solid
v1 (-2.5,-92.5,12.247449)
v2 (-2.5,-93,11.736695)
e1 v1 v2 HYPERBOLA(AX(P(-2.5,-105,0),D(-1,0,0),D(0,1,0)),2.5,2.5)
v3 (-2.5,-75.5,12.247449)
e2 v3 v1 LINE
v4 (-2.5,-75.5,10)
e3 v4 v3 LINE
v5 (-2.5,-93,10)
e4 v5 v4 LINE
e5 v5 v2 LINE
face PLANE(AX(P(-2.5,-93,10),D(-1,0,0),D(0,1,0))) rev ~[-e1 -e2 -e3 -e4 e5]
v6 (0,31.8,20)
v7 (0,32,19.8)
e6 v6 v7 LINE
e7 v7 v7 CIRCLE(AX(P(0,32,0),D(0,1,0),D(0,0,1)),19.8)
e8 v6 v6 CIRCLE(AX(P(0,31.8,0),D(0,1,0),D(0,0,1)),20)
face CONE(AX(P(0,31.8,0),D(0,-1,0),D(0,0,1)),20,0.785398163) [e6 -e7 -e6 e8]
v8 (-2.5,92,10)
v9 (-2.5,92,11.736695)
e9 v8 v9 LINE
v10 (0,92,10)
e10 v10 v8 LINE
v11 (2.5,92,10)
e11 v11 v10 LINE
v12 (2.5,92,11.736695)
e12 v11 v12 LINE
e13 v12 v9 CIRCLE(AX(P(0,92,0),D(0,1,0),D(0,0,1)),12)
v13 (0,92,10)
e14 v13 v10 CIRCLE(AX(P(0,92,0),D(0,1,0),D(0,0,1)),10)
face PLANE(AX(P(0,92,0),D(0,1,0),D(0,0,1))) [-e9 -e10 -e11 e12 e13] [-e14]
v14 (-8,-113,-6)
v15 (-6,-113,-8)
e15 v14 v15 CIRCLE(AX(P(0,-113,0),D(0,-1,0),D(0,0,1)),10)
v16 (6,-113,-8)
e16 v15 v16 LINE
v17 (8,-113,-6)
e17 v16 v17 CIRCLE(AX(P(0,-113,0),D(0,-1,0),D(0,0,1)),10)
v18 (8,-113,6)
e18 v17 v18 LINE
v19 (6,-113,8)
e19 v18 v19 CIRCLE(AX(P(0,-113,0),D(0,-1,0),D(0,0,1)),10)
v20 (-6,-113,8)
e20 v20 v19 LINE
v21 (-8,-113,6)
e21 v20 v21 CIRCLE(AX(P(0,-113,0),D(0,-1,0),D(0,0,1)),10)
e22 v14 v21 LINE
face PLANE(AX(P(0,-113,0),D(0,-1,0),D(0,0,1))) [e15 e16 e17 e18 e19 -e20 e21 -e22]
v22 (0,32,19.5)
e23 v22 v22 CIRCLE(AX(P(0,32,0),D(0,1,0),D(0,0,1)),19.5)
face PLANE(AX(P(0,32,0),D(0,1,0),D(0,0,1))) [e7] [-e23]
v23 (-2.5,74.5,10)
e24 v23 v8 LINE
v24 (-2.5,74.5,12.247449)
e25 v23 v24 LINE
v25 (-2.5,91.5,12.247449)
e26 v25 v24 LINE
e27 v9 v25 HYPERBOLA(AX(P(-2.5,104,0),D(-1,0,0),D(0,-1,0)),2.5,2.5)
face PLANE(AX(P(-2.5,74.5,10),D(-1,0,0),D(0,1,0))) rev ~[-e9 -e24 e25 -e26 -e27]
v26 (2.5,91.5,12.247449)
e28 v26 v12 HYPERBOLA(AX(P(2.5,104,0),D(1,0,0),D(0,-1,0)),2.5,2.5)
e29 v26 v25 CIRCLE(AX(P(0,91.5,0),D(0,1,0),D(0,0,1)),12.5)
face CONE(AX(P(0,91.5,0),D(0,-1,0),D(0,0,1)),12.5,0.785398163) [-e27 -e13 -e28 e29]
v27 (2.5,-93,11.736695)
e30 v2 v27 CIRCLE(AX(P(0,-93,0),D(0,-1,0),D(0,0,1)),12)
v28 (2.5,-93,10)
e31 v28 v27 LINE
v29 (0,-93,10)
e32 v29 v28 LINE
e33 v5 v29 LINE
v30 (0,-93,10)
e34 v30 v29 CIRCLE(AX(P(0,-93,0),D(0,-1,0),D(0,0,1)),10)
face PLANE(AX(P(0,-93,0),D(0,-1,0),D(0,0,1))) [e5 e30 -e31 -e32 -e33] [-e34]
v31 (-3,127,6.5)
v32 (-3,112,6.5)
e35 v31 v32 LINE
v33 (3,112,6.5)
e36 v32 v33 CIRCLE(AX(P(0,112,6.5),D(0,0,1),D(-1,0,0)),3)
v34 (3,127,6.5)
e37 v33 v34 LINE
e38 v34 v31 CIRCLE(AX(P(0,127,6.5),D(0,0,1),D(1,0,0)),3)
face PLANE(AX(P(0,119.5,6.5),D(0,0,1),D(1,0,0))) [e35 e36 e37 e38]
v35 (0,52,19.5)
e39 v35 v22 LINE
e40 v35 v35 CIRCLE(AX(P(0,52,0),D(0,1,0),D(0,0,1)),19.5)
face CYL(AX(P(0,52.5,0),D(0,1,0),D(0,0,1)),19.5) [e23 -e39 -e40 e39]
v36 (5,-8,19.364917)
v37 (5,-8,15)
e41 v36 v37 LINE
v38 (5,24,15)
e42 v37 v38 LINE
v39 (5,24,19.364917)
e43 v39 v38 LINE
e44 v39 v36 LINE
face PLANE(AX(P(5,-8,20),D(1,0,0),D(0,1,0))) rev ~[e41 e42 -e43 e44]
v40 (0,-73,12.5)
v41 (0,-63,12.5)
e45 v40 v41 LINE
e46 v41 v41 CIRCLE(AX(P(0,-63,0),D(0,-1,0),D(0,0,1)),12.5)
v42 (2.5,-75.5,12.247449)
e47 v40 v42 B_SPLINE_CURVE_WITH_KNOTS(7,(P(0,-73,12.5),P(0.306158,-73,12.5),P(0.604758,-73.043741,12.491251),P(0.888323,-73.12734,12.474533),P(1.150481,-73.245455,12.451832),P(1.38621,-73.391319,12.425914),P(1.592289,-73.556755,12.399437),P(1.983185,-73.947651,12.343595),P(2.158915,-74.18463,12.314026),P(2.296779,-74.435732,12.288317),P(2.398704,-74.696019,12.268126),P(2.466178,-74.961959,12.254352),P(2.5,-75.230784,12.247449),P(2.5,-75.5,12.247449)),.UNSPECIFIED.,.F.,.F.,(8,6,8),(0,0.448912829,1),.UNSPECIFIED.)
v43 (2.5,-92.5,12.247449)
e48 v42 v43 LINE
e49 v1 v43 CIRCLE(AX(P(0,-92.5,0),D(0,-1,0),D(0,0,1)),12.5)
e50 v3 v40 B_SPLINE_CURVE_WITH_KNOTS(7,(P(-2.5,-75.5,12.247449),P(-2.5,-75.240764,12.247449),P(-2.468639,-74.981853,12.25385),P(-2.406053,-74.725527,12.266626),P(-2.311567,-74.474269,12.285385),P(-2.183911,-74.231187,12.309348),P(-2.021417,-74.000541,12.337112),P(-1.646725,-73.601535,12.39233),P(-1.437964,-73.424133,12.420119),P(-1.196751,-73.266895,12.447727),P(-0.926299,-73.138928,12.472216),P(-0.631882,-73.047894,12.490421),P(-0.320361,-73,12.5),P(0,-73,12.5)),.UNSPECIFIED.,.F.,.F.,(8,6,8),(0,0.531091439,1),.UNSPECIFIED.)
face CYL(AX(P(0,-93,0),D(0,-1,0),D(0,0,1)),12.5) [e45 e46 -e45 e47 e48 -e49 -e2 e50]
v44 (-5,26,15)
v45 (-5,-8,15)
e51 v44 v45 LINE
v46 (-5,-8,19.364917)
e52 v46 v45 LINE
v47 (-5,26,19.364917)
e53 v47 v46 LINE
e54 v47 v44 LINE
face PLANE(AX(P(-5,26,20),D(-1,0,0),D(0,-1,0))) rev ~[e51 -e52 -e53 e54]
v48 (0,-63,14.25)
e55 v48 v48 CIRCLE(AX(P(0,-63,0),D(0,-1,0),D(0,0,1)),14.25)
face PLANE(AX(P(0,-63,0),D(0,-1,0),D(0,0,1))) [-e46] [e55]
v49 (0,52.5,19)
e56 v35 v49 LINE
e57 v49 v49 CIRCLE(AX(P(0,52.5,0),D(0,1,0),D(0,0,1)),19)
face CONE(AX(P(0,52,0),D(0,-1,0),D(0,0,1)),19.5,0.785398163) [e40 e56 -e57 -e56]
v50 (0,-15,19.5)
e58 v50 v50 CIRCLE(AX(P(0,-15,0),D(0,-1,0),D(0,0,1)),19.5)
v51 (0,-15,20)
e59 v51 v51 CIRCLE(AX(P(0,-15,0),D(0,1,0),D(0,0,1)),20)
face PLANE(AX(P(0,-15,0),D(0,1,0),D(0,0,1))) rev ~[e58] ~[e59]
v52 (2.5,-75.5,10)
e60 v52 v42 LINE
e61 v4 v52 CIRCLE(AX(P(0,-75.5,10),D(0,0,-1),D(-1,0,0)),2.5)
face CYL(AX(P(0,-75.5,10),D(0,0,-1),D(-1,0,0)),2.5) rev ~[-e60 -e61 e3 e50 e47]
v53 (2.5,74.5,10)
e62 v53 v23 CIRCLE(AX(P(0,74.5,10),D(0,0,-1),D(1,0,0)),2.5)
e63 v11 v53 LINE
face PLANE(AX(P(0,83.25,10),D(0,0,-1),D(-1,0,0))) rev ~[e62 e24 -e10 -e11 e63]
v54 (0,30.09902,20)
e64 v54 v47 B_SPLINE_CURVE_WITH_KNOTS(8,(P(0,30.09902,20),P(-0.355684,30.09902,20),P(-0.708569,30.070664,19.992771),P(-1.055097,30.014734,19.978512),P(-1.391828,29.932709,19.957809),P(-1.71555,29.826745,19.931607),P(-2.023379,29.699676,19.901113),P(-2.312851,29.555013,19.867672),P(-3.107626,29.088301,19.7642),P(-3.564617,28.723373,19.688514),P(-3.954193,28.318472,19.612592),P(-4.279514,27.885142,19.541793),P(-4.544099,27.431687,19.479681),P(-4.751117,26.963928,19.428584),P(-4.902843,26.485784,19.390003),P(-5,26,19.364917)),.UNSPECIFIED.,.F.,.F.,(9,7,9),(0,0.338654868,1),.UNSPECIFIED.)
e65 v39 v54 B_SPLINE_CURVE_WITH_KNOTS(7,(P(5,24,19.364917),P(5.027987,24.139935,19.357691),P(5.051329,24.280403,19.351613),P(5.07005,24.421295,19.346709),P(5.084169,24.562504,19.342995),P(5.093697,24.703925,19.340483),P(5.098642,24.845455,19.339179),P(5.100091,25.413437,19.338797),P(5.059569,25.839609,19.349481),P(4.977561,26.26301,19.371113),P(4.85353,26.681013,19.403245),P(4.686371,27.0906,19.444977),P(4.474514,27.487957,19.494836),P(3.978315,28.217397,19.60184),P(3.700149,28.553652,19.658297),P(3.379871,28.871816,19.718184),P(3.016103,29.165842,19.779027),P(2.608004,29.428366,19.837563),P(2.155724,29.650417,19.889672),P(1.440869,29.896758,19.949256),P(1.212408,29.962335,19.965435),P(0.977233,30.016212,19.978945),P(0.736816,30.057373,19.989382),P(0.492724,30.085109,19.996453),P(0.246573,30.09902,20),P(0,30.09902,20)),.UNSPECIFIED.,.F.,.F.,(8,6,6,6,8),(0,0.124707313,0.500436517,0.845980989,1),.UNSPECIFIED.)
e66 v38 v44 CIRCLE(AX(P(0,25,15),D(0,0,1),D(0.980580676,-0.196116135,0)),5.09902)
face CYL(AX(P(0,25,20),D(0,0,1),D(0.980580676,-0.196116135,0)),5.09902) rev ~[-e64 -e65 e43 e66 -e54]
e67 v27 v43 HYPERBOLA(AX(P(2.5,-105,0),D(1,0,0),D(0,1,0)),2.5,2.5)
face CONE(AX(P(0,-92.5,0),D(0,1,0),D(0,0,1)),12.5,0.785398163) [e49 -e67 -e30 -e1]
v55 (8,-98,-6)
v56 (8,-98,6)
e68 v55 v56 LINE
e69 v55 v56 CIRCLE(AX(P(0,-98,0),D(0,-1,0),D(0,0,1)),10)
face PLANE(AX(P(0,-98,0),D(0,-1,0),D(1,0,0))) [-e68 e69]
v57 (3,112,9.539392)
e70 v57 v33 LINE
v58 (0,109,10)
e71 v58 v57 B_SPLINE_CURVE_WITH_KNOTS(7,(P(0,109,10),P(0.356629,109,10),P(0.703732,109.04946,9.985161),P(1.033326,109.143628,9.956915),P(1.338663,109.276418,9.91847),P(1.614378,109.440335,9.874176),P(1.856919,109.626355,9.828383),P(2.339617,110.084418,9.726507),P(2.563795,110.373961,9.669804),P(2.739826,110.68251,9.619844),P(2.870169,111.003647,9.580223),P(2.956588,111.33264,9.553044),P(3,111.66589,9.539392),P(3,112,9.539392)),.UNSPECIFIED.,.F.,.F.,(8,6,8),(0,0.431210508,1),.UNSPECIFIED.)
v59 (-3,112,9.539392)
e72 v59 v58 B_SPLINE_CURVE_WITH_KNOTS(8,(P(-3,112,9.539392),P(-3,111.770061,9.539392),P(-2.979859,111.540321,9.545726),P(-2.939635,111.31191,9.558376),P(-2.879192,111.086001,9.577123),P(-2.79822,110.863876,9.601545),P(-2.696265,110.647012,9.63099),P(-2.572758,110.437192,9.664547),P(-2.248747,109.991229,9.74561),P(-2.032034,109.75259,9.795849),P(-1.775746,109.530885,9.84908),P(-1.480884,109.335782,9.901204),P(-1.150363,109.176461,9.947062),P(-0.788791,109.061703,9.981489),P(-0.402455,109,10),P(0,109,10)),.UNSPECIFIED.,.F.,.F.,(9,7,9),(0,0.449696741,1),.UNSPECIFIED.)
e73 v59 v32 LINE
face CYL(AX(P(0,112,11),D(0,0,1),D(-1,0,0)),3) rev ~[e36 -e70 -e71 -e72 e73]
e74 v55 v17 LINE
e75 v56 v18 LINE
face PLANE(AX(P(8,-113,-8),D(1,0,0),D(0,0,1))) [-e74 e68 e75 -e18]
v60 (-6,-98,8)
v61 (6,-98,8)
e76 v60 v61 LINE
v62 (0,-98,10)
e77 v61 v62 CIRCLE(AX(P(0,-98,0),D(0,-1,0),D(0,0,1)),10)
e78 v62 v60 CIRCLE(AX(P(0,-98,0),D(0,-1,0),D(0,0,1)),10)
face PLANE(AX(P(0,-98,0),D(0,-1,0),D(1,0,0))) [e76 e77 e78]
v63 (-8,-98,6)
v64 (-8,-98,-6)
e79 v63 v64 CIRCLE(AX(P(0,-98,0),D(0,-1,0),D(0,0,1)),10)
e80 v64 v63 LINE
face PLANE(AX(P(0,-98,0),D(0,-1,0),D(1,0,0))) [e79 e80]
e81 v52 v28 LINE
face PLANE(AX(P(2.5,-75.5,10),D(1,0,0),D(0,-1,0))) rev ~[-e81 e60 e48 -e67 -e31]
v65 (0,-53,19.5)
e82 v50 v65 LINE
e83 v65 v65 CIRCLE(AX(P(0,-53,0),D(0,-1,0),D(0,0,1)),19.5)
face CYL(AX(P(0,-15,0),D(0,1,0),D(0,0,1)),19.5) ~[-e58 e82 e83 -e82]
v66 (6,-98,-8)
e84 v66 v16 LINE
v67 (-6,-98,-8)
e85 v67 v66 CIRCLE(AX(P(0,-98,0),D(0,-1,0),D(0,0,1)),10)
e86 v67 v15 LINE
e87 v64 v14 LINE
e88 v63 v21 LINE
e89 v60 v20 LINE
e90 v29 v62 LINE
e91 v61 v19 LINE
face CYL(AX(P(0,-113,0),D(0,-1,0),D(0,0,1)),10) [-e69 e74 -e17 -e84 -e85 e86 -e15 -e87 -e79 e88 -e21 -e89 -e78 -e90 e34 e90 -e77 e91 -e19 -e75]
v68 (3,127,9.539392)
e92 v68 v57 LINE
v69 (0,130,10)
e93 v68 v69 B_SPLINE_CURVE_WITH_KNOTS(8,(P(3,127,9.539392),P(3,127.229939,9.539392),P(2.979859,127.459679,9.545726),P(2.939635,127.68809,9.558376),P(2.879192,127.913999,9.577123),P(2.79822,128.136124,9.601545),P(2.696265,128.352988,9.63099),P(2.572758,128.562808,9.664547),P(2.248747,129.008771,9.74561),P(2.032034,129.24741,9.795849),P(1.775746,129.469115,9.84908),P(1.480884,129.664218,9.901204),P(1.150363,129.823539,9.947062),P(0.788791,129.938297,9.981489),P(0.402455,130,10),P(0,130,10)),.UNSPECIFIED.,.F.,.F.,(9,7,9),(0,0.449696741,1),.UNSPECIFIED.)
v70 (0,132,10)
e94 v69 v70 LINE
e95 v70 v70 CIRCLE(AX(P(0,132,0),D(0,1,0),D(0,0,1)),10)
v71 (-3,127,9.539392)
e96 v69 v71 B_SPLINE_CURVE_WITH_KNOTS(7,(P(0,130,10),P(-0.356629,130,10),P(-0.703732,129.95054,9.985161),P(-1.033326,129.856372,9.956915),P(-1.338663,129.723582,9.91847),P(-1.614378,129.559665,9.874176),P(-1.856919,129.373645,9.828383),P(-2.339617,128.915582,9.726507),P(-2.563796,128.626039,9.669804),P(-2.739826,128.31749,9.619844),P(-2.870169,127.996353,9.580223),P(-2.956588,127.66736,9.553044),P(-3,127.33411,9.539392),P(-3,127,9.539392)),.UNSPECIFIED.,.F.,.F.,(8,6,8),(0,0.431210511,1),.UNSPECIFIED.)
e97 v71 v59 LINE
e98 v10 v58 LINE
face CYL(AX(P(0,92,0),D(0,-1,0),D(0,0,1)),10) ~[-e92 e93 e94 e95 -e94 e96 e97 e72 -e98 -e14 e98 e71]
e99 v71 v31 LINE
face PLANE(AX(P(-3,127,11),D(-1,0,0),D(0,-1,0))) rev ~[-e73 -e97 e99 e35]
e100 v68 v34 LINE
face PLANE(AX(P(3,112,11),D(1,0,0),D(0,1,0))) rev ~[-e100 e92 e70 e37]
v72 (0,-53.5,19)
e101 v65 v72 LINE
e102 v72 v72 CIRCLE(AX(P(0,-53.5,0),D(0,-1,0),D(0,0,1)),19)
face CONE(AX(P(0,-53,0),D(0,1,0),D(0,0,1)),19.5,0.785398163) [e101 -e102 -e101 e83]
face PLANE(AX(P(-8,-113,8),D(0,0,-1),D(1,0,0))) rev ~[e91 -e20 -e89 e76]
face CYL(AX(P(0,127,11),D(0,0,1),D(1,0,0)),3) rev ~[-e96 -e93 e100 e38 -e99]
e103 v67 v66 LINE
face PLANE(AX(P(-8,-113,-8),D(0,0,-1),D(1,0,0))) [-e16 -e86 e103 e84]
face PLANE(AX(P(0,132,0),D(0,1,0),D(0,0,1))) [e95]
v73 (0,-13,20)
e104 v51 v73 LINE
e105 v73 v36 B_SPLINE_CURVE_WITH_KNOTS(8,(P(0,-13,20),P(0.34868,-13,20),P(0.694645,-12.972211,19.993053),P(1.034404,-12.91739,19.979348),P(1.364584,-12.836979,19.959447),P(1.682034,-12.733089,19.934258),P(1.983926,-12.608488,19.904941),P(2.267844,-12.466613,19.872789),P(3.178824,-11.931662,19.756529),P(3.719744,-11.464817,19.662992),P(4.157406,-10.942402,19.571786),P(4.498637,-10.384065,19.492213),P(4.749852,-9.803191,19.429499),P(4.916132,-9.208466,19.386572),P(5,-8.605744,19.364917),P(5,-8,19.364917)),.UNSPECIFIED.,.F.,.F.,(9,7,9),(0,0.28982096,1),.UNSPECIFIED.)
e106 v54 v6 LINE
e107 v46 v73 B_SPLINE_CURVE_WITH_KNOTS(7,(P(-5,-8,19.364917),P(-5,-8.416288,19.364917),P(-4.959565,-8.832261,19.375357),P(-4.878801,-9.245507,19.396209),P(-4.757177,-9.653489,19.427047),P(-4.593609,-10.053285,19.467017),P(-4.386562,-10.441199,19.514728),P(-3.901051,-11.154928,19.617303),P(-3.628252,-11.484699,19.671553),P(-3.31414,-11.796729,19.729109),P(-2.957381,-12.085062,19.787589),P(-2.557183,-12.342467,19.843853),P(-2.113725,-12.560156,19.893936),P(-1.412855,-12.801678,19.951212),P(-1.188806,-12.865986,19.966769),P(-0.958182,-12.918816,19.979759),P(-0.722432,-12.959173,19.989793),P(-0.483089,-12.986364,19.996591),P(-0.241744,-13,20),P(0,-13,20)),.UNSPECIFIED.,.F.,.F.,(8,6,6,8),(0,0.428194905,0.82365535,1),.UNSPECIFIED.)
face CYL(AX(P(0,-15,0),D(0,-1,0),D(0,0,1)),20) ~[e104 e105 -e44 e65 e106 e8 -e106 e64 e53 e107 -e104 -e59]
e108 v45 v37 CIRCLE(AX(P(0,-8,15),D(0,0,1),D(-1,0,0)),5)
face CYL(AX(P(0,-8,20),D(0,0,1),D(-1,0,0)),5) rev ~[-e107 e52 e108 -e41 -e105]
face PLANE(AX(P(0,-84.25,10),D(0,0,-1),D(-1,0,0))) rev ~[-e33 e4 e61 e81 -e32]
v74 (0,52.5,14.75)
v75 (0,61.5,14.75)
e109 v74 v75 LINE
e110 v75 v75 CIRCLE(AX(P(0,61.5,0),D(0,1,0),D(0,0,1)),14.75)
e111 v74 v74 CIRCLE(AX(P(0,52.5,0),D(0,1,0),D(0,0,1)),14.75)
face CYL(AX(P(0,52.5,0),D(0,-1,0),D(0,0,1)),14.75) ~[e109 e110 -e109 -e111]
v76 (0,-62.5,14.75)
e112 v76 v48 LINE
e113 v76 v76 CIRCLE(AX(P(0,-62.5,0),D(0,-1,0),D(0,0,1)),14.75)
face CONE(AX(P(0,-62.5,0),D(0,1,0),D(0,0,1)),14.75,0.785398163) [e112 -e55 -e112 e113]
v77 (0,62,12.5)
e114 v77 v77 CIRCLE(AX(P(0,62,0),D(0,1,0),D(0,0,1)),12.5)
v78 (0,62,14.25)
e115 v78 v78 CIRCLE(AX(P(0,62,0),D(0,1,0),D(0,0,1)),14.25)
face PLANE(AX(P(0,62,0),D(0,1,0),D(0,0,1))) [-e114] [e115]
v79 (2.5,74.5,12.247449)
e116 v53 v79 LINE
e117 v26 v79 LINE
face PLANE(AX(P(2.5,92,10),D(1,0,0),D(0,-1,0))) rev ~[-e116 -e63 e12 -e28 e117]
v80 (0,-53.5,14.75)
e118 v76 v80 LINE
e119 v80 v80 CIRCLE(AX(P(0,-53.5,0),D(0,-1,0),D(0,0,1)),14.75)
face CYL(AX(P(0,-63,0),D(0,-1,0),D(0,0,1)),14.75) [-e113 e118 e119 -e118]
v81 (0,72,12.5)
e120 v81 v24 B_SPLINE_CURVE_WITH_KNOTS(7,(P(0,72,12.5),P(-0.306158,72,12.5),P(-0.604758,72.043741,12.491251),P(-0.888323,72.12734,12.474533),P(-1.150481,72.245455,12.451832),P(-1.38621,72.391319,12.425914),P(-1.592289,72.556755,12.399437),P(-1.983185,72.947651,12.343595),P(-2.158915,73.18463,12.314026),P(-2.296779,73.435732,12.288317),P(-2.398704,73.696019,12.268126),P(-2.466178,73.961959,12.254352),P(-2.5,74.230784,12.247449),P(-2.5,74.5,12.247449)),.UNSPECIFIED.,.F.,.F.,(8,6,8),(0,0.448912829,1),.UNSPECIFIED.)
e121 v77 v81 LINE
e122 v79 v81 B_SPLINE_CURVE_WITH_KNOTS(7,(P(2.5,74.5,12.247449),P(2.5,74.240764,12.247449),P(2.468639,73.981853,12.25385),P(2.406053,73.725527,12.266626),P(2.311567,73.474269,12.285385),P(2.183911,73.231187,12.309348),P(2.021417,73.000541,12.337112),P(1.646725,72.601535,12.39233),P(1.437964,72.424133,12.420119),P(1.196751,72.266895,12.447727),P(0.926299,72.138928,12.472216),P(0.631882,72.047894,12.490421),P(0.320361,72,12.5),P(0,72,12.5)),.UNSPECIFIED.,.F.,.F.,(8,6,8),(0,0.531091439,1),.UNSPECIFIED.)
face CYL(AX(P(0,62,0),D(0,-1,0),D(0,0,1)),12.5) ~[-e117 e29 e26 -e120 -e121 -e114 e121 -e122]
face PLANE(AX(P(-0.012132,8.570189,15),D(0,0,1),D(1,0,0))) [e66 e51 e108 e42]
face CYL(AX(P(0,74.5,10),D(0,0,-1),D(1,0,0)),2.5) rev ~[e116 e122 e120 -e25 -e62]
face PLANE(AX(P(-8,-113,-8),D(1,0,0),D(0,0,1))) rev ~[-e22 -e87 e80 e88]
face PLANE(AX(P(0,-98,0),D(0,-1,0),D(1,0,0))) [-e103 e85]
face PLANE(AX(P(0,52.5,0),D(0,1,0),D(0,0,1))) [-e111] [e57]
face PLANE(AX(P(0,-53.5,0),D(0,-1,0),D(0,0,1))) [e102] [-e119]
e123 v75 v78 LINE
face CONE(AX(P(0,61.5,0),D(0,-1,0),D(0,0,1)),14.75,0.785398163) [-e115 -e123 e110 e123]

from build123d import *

# Parameters (mm, degrees)
EXTRUDE1_DEPTH       = 32
EXTRUDE1_DEPTH_BACK  = 15
SKETCH1_R            = 20
SKETCH_1_R           = 19.5
EXTRUDE_1_DEPTH      = 38.5
EXTRUDE2_START       = 20.5
SKETCH2_R            = 19.5
EXTRUDE2_DEPTH       = 20.5
CHAMFER1_SIZE        = 0.2
CUT_EXTRUDE1_DEPTH   = 5
SKETCH5_R            = 14.75
EXTRUDE3_DEPTH       = 9.5
SKETCH6_R            = 12.5
EXTRUDE4_DEPTH       = 30
EXTRUDE5_START       = 9.5
SKETCH7_R            = 14.75
EXTRUDE5_DEPTH       = 9.5
EXTRUDE6_START       = 30
SKETCH8_R            = 12.5
EXTRUDE6_DEPTH       = 30
CHAMFER2_SIZE        = 0.5
SKETCH9_R            = 10
EXTRUDE7_DEPTH       = 40
CUT_EXTRUDE2_DEPTH   = 4.5
BOSS_EXTRUDE1_START  = 20
SKETCH11_R           = 10
BOSS_EXTRUDE1_DEPTH  = 20
SKETCH12_OUTSIDE_W   = 92.29
SKETCH12_OUTSIDE_H   = 92.29
SKETCH12_OUTSIDE_W_2 = 16
SKETCH12_OUTSIDE_H_2 = 16
CUT_EXTRUDE3_DEPTH   = 15
CHAMFER3_SIZE        = 0.5
CUT_EXTRUDE4_DEPTH   = 10


with BuildPart() as part:
    # Sketch1 → Extrude1 (new, two sides: drawn at the far end of the back side and taken through both)
    with BuildSketch(Plane(origin=(0, 0, 0), x_dir=(1, 0, 0), z_dir=(0, 1, 0)).offset(-EXTRUDE1_DEPTH_BACK)):
        with Locations(Location((0, 0, 0), (0, 0, 270))):
            Circle(SKETCH1_R)
    extrude(amount=EXTRUDE1_DEPTH + EXTRUDE1_DEPTH_BACK)

    # 草图1 → 拉伸1 (add)
    with BuildSketch(Plane.XZ.offset(15)):
        with Locations(Location((0, 0, 0), (0, 0, 90))):
            Circle(SKETCH_1_R)
    extrude(amount=EXTRUDE_1_DEPTH)

    # Sketch2 → Extrude2 (add)
    with BuildSketch(Plane(origin=(0, 32, 0), x_dir=(1, 0, 0), z_dir=(0, 1, 0)).offset(EXTRUDE2_START)):
        with Locations(Location((0, 0, 0), (0, 0, 270))):
            Circle(SKETCH2_R)
    extrude(amount=-EXTRUDE2_DEPTH)

    # Chamfer1
    chamfer1_edges = [part.edges().sort_by_distance(p)[0] for p in [
        (0, 32, -20),
    ]]
    chamfer(chamfer1_edges, length=CHAMFER1_SIZE)

    # Sketch4 → Cut-Extrude1 (cut)
    with BuildSketch(Plane.XY.offset(20)):
        with BuildLine():
            Line((-5, 26), (-5, -8))
            ThreePointArc((-5, -8), (0, -13), (5, -8))
            Line((5, -8), (5, 24))
            ThreePointArc((5, 24), (1, 30), (-5, 26))
        make_face()
    extrude(amount=-CUT_EXTRUDE1_DEPTH, mode=Mode.SUBTRACT)

    # Sketch5 → Extrude3 (add)
    with BuildSketch(Plane(origin=(0, 52.5, 0), x_dir=(1, 0, 0), z_dir=(0, 1, 0))):
        with Locations(Location((0, 0, 0), (0, 0, 270))):
            Circle(SKETCH5_R)
    extrude(amount=EXTRUDE3_DEPTH)

    # Sketch6 → Extrude4 (add)
    with BuildSketch(Plane(origin=(0, 62, 0), x_dir=(1, 0, 0), z_dir=(0, 1, 0))):
        with Locations(Location((0, 0, 0), (0, 0, 270))):
            Circle(SKETCH6_R)
    extrude(amount=EXTRUDE4_DEPTH)

    # Sketch7 → Extrude5 (add)
    with BuildSketch(Plane.XZ.offset(53.5).offset(EXTRUDE5_START)):
        with Locations(Location((0, 0, 0), (0, 0, 90))):
            Circle(SKETCH7_R)
    extrude(amount=-EXTRUDE5_DEPTH)

    # Sketch8 → Extrude6 (add)
    with BuildSketch(Plane.XZ.offset(63).offset(EXTRUDE6_START)):
        with Locations(Location((0, 0, 0), (0, 0, 90))):
            Circle(SKETCH8_R)
    extrude(amount=-EXTRUDE6_DEPTH)

    # Chamfer2
    chamfer2_edges = [part.edges().sort_by_distance(p)[0] for p in [
        (0, 52.5, -19.5),
        (0, 62, -14.75),
        (0, 92, -12.5),
        (0, -63, -14.75),
        (0, -53.5, -19.5),
    ]]
    chamfer(chamfer2_edges, length=CHAMFER2_SIZE)

    # Sketch9 → Extrude7 (add)
    with BuildSketch(Plane(origin=(0, 92, 0), x_dir=(1, 0, 0), z_dir=(0, 1, 0))):
        with Locations(Location((0, 0, 0), (0, 0, 270))):
            Circle(SKETCH9_R)
    extrude(amount=EXTRUDE7_DEPTH)

    # Sketch10 → Cut-Extrude2 (cut)
    with BuildSketch(Plane.XY.offset(11)):
        with BuildLine():
            Line((-3, 127), (-3, 112))
            ThreePointArc((-3, 112), (0, 109), (3, 112))
            Line((3, 112), (3, 127))
            ThreePointArc((3, 127), (0, 130), (-3, 127))
        make_face()
    extrude(amount=-CUT_EXTRUDE2_DEPTH, mode=Mode.SUBTRACT)

    # Sketch11 → Boss-Extrude1 (add)
    with BuildSketch(Plane.XZ.offset(93).offset(BOSS_EXTRUDE1_START)):
        with Locations(Location((0, 0, 0), (0, 0, 90))):
            Circle(SKETCH11_R)
    extrude(amount=-BOSS_EXTRUDE1_DEPTH)

    # Sketch12 outside → Cut-Extrude3 (cut)
    with BuildSketch(Plane.XZ.offset(113)):
        Rectangle(SKETCH12_OUTSIDE_W, SKETCH12_OUTSIDE_H)
        Rectangle(SKETCH12_OUTSIDE_W_2, SKETCH12_OUTSIDE_H_2, mode=Mode.SUBTRACT)
    extrude(amount=-CUT_EXTRUDE3_DEPTH, mode=Mode.SUBTRACT)

    # Chamfer3
    chamfer3_edges = [part.edges().sort_by_distance(p)[0] for p in [
        (0, -93, -12.5),
    ]]
    chamfer(chamfer3_edges, length=CHAMFER3_SIZE)

    # Sketch13 → Cut-Extrude4 (cut)
    with BuildSketch(Plane.XY.offset(10)):
        with BuildLine():
            Line((2.5, 92), (2.5, 74.5))
            ThreePointArc((2.5, 74.5), (0, 72), (-2.5, 74.5))
            Line((-2.5, 74.5), (-2.5, 92))
            ThreePointArc((-2.5, 92), (0, 94.5), (2.5, 92))
        make_face()
        with BuildLine():
            Line((-2.5, -93), (-2.5, -75.5))
            ThreePointArc((-2.5, -75.5), (0, -73), (2.5, -75.5))
            Line((2.5, -75.5), (2.5, -93))
            ThreePointArc((2.5, -93), (0, -95.5), (-2.5, -93))
        make_face()
    extrude(amount=CUT_EXTRUDE4_DEPTH, mode=Mode.SUBTRACT)


solid = part.part
